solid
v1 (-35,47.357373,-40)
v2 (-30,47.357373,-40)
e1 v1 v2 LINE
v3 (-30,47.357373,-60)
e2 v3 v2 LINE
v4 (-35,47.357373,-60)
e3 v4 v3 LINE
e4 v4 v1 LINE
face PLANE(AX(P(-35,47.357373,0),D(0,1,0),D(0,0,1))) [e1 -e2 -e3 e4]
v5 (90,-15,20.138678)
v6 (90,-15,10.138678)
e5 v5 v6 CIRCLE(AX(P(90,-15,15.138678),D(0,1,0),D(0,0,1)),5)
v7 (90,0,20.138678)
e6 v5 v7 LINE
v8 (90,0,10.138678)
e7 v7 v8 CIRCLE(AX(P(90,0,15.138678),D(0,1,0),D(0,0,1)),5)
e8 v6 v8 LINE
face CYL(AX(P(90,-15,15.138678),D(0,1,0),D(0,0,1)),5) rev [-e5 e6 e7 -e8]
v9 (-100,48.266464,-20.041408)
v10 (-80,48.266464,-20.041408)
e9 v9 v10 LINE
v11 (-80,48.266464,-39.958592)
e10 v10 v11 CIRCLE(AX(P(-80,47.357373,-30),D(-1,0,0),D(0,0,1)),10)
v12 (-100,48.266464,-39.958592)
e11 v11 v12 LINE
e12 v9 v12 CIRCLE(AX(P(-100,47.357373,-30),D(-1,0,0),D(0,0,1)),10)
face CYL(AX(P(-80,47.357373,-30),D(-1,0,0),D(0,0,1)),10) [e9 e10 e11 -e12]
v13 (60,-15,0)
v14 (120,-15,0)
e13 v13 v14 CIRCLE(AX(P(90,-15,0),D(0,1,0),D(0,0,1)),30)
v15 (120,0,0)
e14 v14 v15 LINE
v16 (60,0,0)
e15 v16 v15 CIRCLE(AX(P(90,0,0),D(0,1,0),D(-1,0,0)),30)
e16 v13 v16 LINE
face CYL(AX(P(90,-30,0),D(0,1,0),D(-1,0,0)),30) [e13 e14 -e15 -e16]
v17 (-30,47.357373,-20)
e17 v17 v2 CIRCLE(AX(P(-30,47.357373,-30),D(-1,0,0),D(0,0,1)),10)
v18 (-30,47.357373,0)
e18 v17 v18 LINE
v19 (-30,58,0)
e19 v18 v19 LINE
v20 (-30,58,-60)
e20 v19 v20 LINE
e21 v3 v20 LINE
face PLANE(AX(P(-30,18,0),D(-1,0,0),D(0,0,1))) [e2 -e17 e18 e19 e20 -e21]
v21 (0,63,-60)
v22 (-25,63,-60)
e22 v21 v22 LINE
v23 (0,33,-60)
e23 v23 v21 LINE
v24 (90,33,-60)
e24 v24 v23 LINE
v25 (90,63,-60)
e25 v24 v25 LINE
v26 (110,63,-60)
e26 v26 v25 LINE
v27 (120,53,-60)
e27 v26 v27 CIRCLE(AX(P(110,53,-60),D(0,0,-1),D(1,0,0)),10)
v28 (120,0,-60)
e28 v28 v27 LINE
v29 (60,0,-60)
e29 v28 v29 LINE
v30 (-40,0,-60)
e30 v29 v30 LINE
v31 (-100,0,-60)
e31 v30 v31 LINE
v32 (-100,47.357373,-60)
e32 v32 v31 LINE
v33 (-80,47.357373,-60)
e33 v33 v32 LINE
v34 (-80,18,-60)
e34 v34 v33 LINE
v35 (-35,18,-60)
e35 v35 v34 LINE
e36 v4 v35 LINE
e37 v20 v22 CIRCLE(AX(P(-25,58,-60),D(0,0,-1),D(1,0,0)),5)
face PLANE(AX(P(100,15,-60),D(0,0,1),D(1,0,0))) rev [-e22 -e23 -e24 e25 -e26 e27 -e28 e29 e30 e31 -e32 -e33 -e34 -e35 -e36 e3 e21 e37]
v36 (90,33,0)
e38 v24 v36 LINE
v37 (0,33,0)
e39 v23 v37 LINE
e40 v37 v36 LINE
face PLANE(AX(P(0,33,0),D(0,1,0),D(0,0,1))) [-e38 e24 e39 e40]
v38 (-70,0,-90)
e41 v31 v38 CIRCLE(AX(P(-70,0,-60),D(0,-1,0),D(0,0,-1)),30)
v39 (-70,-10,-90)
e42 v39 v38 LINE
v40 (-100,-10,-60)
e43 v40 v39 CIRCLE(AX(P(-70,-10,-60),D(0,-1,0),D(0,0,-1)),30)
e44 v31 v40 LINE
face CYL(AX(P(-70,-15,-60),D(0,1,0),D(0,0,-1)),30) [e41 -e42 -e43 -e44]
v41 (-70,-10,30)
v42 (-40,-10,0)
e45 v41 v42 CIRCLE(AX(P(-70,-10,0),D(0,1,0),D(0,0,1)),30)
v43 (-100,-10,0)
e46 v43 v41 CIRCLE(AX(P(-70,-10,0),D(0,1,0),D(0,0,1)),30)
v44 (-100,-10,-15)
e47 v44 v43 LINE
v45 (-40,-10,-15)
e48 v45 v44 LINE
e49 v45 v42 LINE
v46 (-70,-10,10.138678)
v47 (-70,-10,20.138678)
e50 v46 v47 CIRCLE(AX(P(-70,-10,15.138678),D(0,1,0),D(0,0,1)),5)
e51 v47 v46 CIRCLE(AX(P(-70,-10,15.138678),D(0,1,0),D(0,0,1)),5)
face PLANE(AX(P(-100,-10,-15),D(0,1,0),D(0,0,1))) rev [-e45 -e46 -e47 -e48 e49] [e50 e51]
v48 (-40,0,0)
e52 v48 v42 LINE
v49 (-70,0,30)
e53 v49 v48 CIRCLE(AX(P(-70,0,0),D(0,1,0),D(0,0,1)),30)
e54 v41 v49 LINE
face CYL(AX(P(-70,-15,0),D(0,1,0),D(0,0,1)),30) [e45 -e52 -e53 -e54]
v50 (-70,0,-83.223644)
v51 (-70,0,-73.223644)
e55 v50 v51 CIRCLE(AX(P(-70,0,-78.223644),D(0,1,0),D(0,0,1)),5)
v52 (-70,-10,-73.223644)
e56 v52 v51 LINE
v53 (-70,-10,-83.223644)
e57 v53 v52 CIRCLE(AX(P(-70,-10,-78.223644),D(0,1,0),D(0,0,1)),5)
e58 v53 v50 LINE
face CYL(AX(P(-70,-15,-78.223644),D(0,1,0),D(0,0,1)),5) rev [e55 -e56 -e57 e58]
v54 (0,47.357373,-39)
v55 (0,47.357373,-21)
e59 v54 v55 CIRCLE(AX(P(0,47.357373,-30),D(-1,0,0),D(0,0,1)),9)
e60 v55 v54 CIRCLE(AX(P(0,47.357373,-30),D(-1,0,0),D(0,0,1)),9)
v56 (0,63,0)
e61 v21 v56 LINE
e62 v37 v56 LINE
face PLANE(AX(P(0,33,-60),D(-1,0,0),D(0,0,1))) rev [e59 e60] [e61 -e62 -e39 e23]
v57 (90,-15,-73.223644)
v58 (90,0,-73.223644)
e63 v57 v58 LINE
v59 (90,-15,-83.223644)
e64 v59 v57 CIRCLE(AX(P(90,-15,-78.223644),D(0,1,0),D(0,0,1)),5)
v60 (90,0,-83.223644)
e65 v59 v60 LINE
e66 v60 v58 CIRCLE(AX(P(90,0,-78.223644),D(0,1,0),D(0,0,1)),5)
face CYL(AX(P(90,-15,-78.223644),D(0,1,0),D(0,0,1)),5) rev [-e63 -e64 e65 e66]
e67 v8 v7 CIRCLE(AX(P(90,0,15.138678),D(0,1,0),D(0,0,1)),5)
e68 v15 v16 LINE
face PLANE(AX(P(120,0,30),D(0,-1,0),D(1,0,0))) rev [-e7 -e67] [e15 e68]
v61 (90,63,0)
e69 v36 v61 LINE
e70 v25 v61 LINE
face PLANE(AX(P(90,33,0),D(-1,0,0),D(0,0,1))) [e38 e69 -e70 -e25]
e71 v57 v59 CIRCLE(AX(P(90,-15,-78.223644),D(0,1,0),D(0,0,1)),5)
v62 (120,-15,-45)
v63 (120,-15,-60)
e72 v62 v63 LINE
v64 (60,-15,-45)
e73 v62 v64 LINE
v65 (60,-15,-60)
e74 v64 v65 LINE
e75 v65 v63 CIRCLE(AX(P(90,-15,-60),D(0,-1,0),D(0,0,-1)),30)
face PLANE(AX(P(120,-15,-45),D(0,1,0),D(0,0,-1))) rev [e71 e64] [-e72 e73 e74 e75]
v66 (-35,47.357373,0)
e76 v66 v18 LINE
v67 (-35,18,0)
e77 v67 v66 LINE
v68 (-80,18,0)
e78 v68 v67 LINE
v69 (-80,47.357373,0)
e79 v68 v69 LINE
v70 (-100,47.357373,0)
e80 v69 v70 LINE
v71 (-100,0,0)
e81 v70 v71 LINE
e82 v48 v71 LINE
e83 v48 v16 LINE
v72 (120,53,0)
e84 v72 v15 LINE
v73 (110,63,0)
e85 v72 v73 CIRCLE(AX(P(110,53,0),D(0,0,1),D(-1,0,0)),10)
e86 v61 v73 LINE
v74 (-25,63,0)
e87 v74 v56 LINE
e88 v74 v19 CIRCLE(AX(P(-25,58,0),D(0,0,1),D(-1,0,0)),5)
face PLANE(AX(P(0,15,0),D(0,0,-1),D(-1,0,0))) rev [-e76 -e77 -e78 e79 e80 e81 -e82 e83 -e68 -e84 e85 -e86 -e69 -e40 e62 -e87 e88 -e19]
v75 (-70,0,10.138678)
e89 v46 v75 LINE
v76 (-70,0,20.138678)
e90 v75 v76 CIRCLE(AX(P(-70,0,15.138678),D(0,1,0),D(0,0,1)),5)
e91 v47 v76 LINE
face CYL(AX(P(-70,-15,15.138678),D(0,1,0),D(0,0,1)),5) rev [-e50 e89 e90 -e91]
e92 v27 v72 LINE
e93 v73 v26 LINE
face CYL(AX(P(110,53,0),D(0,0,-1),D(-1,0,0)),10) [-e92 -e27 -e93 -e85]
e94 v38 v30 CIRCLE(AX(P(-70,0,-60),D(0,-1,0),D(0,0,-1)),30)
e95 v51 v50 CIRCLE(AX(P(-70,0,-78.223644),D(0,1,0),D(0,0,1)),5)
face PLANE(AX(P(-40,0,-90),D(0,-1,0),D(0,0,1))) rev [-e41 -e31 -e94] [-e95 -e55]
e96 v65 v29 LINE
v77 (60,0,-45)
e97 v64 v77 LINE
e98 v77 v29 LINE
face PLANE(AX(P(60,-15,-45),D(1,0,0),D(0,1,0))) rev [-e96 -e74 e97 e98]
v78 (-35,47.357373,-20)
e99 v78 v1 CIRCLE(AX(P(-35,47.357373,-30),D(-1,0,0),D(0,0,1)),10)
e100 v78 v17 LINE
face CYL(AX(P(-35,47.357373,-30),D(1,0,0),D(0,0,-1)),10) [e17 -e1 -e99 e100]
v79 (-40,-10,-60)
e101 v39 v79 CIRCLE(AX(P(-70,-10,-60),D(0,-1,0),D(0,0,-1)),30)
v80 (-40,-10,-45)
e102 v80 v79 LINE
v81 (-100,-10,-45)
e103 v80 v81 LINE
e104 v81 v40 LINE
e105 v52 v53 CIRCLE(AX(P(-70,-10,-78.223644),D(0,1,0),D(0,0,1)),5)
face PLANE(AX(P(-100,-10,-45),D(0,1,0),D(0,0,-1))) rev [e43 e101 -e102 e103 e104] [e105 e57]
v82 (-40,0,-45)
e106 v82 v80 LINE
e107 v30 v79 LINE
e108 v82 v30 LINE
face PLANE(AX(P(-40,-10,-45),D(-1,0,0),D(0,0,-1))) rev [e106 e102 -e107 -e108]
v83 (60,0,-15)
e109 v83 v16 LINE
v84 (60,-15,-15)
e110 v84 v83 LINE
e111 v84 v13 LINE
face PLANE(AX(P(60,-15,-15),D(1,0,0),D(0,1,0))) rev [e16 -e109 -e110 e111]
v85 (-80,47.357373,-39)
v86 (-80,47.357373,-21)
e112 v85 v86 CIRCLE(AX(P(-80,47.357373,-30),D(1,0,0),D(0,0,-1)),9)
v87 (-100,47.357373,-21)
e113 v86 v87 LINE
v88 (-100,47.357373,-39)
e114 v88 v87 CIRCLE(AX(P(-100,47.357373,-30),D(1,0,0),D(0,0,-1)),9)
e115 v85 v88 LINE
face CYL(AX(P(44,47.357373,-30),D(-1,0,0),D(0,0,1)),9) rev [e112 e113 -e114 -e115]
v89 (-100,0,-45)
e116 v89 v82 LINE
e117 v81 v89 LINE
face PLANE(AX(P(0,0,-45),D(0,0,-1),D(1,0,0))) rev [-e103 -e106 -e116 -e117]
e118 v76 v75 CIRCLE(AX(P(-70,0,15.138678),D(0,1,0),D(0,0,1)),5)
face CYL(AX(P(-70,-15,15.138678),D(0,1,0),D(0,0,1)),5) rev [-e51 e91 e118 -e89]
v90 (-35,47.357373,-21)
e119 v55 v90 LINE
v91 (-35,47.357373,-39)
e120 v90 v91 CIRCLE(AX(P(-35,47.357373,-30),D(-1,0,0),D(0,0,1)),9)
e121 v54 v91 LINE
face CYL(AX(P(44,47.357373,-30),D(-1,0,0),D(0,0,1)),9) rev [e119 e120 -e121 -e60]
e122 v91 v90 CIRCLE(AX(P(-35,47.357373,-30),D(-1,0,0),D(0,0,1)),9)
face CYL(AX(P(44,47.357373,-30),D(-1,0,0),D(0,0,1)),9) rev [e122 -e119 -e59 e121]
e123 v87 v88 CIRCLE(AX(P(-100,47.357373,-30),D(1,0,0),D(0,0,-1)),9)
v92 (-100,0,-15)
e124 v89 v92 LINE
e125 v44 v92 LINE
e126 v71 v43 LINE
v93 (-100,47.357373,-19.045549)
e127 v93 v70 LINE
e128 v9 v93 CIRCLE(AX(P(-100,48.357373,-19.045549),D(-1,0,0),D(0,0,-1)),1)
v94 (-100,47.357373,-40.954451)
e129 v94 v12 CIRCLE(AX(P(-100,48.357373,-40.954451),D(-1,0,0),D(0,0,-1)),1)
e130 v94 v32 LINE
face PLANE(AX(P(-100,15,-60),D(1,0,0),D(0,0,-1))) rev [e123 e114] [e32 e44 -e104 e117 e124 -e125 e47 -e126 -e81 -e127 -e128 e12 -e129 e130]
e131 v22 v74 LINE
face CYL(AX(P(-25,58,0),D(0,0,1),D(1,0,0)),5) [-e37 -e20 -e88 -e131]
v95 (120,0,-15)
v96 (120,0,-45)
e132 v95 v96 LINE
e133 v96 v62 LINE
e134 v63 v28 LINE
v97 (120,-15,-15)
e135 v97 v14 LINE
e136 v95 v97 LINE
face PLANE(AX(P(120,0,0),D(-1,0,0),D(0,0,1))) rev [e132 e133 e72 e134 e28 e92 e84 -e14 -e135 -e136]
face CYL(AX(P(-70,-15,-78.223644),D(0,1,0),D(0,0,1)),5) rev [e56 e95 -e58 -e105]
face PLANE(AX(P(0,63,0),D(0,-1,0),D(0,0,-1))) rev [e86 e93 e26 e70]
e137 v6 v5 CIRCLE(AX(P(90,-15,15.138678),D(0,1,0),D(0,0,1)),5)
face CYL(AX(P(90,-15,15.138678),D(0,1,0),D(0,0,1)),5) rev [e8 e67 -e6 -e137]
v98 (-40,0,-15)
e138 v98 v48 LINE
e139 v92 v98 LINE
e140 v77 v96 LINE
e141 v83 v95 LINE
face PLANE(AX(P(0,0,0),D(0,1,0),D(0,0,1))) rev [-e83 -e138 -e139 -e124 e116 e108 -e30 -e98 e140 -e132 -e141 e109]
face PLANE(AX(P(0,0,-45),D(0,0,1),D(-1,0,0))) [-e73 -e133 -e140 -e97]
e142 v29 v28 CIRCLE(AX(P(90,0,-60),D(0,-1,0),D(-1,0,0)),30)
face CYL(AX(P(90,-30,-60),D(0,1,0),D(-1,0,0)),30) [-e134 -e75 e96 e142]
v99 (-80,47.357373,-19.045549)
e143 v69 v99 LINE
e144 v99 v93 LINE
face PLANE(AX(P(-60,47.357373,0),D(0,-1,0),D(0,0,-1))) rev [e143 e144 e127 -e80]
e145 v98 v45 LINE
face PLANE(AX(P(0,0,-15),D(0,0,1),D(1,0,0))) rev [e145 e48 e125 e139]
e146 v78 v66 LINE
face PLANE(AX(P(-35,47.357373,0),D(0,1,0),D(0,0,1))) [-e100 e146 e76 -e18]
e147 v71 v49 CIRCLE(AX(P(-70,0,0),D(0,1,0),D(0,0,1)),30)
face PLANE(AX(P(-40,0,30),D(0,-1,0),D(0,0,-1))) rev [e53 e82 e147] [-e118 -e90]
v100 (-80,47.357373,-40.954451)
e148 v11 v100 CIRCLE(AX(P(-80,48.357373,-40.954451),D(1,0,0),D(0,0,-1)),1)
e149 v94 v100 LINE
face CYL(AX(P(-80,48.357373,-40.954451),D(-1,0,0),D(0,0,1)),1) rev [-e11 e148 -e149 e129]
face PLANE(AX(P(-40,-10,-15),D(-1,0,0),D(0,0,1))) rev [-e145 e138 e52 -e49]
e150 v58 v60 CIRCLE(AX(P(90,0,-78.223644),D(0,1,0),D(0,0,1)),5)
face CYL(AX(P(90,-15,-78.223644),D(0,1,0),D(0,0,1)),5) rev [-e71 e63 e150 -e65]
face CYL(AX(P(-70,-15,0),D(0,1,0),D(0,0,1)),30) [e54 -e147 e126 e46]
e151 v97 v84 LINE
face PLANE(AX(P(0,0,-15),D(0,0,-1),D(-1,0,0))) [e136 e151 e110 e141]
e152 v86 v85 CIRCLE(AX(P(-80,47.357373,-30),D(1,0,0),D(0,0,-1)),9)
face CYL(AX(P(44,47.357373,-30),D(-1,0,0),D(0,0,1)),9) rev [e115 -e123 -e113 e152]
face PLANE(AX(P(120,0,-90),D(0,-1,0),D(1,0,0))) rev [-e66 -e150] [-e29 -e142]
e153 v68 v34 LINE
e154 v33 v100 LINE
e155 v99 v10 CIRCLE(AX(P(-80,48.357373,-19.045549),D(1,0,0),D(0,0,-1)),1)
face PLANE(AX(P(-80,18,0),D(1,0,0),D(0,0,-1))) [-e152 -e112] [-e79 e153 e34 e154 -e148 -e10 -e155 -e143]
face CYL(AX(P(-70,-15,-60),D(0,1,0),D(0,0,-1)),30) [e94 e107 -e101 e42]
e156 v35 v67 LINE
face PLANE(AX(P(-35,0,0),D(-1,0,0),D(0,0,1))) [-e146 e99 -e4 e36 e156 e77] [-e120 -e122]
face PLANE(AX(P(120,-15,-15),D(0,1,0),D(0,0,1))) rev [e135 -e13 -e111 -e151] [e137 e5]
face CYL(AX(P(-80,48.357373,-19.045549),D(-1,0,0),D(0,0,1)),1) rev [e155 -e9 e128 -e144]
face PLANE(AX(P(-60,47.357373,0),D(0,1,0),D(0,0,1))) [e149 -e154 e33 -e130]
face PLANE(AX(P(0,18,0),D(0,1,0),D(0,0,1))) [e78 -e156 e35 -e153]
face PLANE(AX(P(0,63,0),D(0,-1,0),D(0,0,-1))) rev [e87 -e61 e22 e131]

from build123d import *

# Parameters (mm, degrees)
BASE_PLATE_DEPTH           = 15
BODY_BLOCK_SKETCH_W        = 200
BODY_BLOCK_SKETCH_H        = 60
BODY_BLOCK_DEPTH           = 48
FIXED_JAW_SKETCH_W         = 60
FIXED_JAW_SKETCH_H         = 63
FIXED_JAW_DEPTH            = 20
GUIDE_CHANNEL_SKETCH_W     = 60
GUIDE_CHANNEL_SKETCH_H     = 60
GUIDE_CHANNEL_CUT_DEPTH    = 30
CHANNEL_END_CUT_SKETCH_W   = 30
CHANNEL_END_CUT_SKETCH_H   = 60
CHANNEL_END_CUT_DEPTH      = 30
JAW_SLOT_SKETCH_W          = 50
JAW_SLOT_SKETCH_H          = 60
JAW_SLOT_CUT_DEPTH         = 45
SLOT_RAIL_SKETCH_R         = 10
SLOT_RAIL_DEPTH            = 5
SCREW_BORE_SKETCH_R        = 9
SCREW_BORE_DEPTH           = 79
SCREW_POCKET_CUT_DEPTH     = 40
SCREW_BOSS_SKETCH_R        = 10
SCREW_BOSS_SKETCH_R_2      = 9
SCREW_BOSS_DEPTH           = 20
FIXED_JAW_FILLET_R10_R     = 10
JAW_SLOT_FILLET_R5_R       = 5
SCREW_BOSS_FILLET_R1_A_R   = 1
SCREW_BOSS_FILLET_R1_B_R   = 1
MOUNTING_FLANGE_SKETCH_W   = 60
MOUNTING_FLANGE_SKETCH_H   = 10
MOUNTING_FLANGE_DEPTH      = 30
FLANGE_RECESS_CUT_DEPTH    = 15
MOUNTING_LUG_SKETCH_W      = 60
MOUNTING_LUG_SKETCH_H      = 10
MOUNTING_LUG_DEPTH         = 15
REAR_JAW_BLOCK_SKETCH_W    = 60
REAR_JAW_BLOCK_SKETCH_H    = 15
REAR_JAW_BLOCK_DEPTH       = 30
REAR_JAW_CHANNEL_CUT_DEPTH = 30
REAR_JAW_NOTCH_CUT_DEPTH   = 30
REAR_LUG_SKETCH_W          = 60
REAR_LUG_SKETCH_H          = 15
REAR_LUG_DEPTH             = 15
LUG_CLEARANCE_CUT_SKETCH_R = 5
LUG_CLEARANCE_CUT_DEPTH    = 15


with BuildPart() as part:
    # Base Plate Sketch → Base Plate (new body)
    with BuildSketch(Plane(origin=(0, 0, 0), x_dir=(1, 0, 0), z_dir=(0, 1, 0))):
        Polygon((0, 0), (100, 0), (100, 60), (-100, 60), (-100, 0), align=None)
    extrude(amount=BASE_PLATE_DEPTH)

    # Body Block Sketch → Body Block (add)
    with BuildSketch(Plane(origin=(0, 15, 0), x_dir=(1, 0, 0), z_dir=(0, 1, 0))):
        with Locations((0, 30)):
            Rectangle(BODY_BLOCK_SKETCH_W, BODY_BLOCK_SKETCH_H)
    extrude(amount=BODY_BLOCK_DEPTH)

    # Fixed Jaw Sketch → Fixed Jaw (add)
    with BuildSketch(Plane(origin=(100, 0, 0), x_dir=(0, 0, -1), z_dir=(1, 0, 0))):
        with Locations((30, 31.5)):
            Rectangle(FIXED_JAW_SKETCH_W, FIXED_JAW_SKETCH_H)
    extrude(amount=FIXED_JAW_DEPTH)

    # Guide Channel Sketch → Guide Channel Cut (cut)
    with BuildSketch(Plane(origin=(0, 63, 0), x_dir=(1, 0, 0), z_dir=(0, 1, 0))):
        with Locations((60, 30)):
            Rectangle(GUIDE_CHANNEL_SKETCH_W, GUIDE_CHANNEL_SKETCH_H)
    extrude(amount=-GUIDE_CHANNEL_CUT_DEPTH, mode=Mode.SUBTRACT)

    # Channel End Cut Sketch → Channel End Cut (cut)
    with BuildSketch(Plane(origin=(0, 63, 0), x_dir=(1, 0, 0), z_dir=(0, 1, 0))):
        with Locations((15, 30)):
            Rectangle(CHANNEL_END_CUT_SKETCH_W, CHANNEL_END_CUT_SKETCH_H)
    extrude(amount=-CHANNEL_END_CUT_DEPTH, mode=Mode.SUBTRACT)

    # Jaw Slot Sketch → Jaw Slot Cut (cut)
    with BuildSketch(Plane(origin=(0, 63, 0), x_dir=(1, 0, 0), z_dir=(0, 1, 0))):
        with Locations((-55, 30)):
            Rectangle(JAW_SLOT_SKETCH_W, JAW_SLOT_SKETCH_H)
    extrude(amount=-JAW_SLOT_CUT_DEPTH, mode=Mode.SUBTRACT)

    # Slot Rail Sketch → Slot Rail (add)
    with BuildSketch(Plane.ZY.offset(30)):
        with Locations((-30, 47.357372748)):
            Circle(SLOT_RAIL_SKETCH_R)
        with BuildLine():
            Line((0, 18), (0, 47.357372748))
            Line((0, 47.357372748), (-20, 47.357372748))
            ThreePointArc((-20, 47.357372748), (-30, 37.357372748), (-40, 47.357372748))
            Line((-40, 47.357372748), (-60, 47.357372748))
            Line((-60, 47.357372748), (-60, 18))
            Line((-60, 18), (0, 18))
        make_face()
    extrude(amount=SLOT_RAIL_DEPTH)

    # Screw Bore Sketch → Screw Bore (cut, symmetric)
    with BuildSketch(Plane.ZY.offset(35)):
        with Locations((-30, 47.357372748)):
            Circle(SCREW_BORE_SKETCH_R)
    extrude(amount=SCREW_BORE_DEPTH, both=True, mode=Mode.SUBTRACT)

    # Screw Pocket Sketch → Screw Pocket Cut (cut)
    with BuildSketch(Plane.ZY.offset(100)):
        with BuildLine():
            ThreePointArc((-39, 47.357372748), (-30, 56.357372748), (-21, 47.357372748))
            Line((-21, 47.357372748), (0, 47.357372748))
            Line((0, 47.357372748), (0, 63))
            Line((0, 63), (-60, 63))
            Line((-60, 63), (-60, 47.357372748))
            Line((-60, 47.357372748), (-39, 47.357372748))
        make_face()
    extrude(amount=-SCREW_POCKET_CUT_DEPTH, mode=Mode.SUBTRACT)

    # Screw Boss Sketch → Screw Boss (add)
    with BuildSketch(Plane.ZY.offset(100)):
        with Locations((-30, 47.357372748)):
            Circle(SCREW_BOSS_SKETCH_R)
        with Locations(Location((-30, 47.357372748, 0), (0, 0, 180))):
            Circle(SCREW_BOSS_SKETCH_R_2, mode=Mode.SUBTRACT)
    extrude(amount=-SCREW_BOSS_DEPTH)

    # Fixed Jaw Fillet R10
    fixed_jaw_fillet_r10_edges = [part.edges().sort_by_distance(p)[0] for p in [
        (120, 63, -30),
    ]]
    fillet(fixed_jaw_fillet_r10_edges, radius=FIXED_JAW_FILLET_R10_R)

    # Jaw Slot Fillet R5
    jaw_slot_fillet_r5_edges = [part.edges().sort_by_distance(p)[0] for p in [
        (-30, 63, -30),
    ]]
    fillet(jaw_slot_fillet_r5_edges, radius=JAW_SLOT_FILLET_R5_R)

    # Screw Boss Fillet R1 A
    screw_boss_fillet_r1_a_edges = [part.edges().sort_by_distance(p)[0] for p in [
        (-90, 47.357372748, -20),
    ]]
    fillet(screw_boss_fillet_r1_a_edges, radius=SCREW_BOSS_FILLET_R1_A_R)

    # Screw Boss Fillet R1 B
    screw_boss_fillet_r1_b_edges = [part.edges().sort_by_distance(p)[0] for p in [
        (-90, 47.357372748, -40),
    ]]
    fillet(screw_boss_fillet_r1_b_edges, radius=SCREW_BOSS_FILLET_R1_B_R)



with BuildPart() as body_2:
    # Mounting Flange Sketch → Mounting Flange (new body)
    with BuildSketch(Plane.XY):
        with Locations((-70, -5)):
            Rectangle(MOUNTING_FLANGE_SKETCH_W, MOUNTING_FLANGE_SKETCH_H)
    extrude(amount=MOUNTING_FLANGE_DEPTH)

    # Flange Recess Sketch → Flange Recess Cut (cut)
    with BuildSketch(Plane(origin=(0, 0, 0), x_dir=(1, 0, 0), z_dir=(0, 1, 0))):
        with BuildLine():
            Line((-40, -30), (-40, 0))
            ThreePointArc((-40, 0), (-48.786796564, -21.213203436), (-70, -30))
            Line((-70, -30), (-40, -30))
        make_face()
        with BuildLine():
            Line((-100, -30), (-70, -30))
            ThreePointArc((-70, -30), (-91.213203436, -21.213203436), (-100, 0))
            Line((-100, 0), (-100, -30))
        make_face()
    extrude(amount=-FLANGE_RECESS_CUT_DEPTH, mode=Mode.SUBTRACT)


with BuildPart() as part_1:
    add(part.part)

    add(body_2.part)  # Mounting Lug merges body 2
    # Mounting Lug Sketch → Mounting Lug (add)
    with BuildSketch(Plane(origin=(0, 0, 0), x_dir=(-1, 0, 0), z_dir=(0, 0, -1))):
        with Locations((70, -5)):
            Rectangle(MOUNTING_LUG_SKETCH_W, MOUNTING_LUG_SKETCH_H)
    extrude(amount=MOUNTING_LUG_DEPTH)

    # Mounting Lug Mirror: part across plane


with BuildPart() as part_2:
    add(part_1.part)
    add(part_1.part.mirror(Plane.XY.offset(-30)))



with BuildPart() as body_2_2:
    # Rear Jaw Block Sketch → Rear Jaw Block (new body)
    with BuildSketch(Plane.XY):
        with Locations((90, -7.5)):
            Rectangle(REAR_JAW_BLOCK_SKETCH_W, REAR_JAW_BLOCK_SKETCH_H)
    extrude(amount=REAR_JAW_BLOCK_DEPTH)

    # Rear Jaw Channel Sketch → Rear Jaw Channel Cut (cut)
    with BuildSketch(Plane(origin=(0, 0, 0), x_dir=(1, 0, 0), z_dir=(0, 1, 0))):
        with BuildLine():
            ThreePointArc((90, -30), (68.786796564, -21.213203436), (60, 0))
            Line((60, 0), (60, -30))
            Line((60, -30), (90, -30))
        make_face()
    extrude(amount=-REAR_JAW_CHANNEL_CUT_DEPTH, mode=Mode.SUBTRACT)

    # Rear Jaw Notch Sketch → Rear Jaw Notch Cut (cut)
    with BuildSketch(Plane(origin=(0, 0, 0), x_dir=(1, 0, 0), z_dir=(0, 1, 0))):
        with BuildLine():
            Line((120, -30), (120, 0))
            ThreePointArc((120, 0), (111.213203436, -21.213203436), (90, -30))
            Line((90, -30), (120, -30))
        make_face()
    extrude(amount=-REAR_JAW_NOTCH_CUT_DEPTH, mode=Mode.SUBTRACT)


with BuildPart() as part_3:
    add(part_2.part)

    add(body_2_2.part)  # Rear Lug merges body 2 2
    # Rear Lug Sketch → Rear Lug (add)
    with BuildSketch(Plane(origin=(0, 0, 0), x_dir=(-1, 0, 0), z_dir=(0, 0, -1))):
        with Locations((-90, -7.5)):
            Rectangle(REAR_LUG_SKETCH_W, REAR_LUG_SKETCH_H)
    extrude(amount=REAR_LUG_DEPTH)

    # Rear Lug Mirror: part across plane


with BuildPart() as part_4:
    add(part_3.part)
    add(part_3.part.mirror(Plane.XY.offset(-30)))

    # Lug Clearance Cut Sketch → Lug Clearance Cut (cut)
    with BuildSketch(Plane(origin=(0, 0, 0), x_dir=(1, 0, 0), z_dir=(0, 1, 0))):
        with Locations(Location((-70, -15.138677931, 0), (0, 0, 270))):
            Circle(LUG_CLEARANCE_CUT_SKETCH_R)
        with Locations(Location((90, -15.138677931, 0), (0, 0, 270))):
            Circle(LUG_CLEARANCE_CUT_SKETCH_R)
        with Locations(Location((-70, 78.223643899, 0), (0, 0, 270))):
            Circle(LUG_CLEARANCE_CUT_SKETCH_R)
        with Locations(Location((90, 78.223643899, 0), (0, 0, 270))):
            Circle(LUG_CLEARANCE_CUT_SKETCH_R)
    extrude(amount=-LUG_CLEARANCE_CUT_DEPTH, mode=Mode.SUBTRACT)


solid = part_4.part
